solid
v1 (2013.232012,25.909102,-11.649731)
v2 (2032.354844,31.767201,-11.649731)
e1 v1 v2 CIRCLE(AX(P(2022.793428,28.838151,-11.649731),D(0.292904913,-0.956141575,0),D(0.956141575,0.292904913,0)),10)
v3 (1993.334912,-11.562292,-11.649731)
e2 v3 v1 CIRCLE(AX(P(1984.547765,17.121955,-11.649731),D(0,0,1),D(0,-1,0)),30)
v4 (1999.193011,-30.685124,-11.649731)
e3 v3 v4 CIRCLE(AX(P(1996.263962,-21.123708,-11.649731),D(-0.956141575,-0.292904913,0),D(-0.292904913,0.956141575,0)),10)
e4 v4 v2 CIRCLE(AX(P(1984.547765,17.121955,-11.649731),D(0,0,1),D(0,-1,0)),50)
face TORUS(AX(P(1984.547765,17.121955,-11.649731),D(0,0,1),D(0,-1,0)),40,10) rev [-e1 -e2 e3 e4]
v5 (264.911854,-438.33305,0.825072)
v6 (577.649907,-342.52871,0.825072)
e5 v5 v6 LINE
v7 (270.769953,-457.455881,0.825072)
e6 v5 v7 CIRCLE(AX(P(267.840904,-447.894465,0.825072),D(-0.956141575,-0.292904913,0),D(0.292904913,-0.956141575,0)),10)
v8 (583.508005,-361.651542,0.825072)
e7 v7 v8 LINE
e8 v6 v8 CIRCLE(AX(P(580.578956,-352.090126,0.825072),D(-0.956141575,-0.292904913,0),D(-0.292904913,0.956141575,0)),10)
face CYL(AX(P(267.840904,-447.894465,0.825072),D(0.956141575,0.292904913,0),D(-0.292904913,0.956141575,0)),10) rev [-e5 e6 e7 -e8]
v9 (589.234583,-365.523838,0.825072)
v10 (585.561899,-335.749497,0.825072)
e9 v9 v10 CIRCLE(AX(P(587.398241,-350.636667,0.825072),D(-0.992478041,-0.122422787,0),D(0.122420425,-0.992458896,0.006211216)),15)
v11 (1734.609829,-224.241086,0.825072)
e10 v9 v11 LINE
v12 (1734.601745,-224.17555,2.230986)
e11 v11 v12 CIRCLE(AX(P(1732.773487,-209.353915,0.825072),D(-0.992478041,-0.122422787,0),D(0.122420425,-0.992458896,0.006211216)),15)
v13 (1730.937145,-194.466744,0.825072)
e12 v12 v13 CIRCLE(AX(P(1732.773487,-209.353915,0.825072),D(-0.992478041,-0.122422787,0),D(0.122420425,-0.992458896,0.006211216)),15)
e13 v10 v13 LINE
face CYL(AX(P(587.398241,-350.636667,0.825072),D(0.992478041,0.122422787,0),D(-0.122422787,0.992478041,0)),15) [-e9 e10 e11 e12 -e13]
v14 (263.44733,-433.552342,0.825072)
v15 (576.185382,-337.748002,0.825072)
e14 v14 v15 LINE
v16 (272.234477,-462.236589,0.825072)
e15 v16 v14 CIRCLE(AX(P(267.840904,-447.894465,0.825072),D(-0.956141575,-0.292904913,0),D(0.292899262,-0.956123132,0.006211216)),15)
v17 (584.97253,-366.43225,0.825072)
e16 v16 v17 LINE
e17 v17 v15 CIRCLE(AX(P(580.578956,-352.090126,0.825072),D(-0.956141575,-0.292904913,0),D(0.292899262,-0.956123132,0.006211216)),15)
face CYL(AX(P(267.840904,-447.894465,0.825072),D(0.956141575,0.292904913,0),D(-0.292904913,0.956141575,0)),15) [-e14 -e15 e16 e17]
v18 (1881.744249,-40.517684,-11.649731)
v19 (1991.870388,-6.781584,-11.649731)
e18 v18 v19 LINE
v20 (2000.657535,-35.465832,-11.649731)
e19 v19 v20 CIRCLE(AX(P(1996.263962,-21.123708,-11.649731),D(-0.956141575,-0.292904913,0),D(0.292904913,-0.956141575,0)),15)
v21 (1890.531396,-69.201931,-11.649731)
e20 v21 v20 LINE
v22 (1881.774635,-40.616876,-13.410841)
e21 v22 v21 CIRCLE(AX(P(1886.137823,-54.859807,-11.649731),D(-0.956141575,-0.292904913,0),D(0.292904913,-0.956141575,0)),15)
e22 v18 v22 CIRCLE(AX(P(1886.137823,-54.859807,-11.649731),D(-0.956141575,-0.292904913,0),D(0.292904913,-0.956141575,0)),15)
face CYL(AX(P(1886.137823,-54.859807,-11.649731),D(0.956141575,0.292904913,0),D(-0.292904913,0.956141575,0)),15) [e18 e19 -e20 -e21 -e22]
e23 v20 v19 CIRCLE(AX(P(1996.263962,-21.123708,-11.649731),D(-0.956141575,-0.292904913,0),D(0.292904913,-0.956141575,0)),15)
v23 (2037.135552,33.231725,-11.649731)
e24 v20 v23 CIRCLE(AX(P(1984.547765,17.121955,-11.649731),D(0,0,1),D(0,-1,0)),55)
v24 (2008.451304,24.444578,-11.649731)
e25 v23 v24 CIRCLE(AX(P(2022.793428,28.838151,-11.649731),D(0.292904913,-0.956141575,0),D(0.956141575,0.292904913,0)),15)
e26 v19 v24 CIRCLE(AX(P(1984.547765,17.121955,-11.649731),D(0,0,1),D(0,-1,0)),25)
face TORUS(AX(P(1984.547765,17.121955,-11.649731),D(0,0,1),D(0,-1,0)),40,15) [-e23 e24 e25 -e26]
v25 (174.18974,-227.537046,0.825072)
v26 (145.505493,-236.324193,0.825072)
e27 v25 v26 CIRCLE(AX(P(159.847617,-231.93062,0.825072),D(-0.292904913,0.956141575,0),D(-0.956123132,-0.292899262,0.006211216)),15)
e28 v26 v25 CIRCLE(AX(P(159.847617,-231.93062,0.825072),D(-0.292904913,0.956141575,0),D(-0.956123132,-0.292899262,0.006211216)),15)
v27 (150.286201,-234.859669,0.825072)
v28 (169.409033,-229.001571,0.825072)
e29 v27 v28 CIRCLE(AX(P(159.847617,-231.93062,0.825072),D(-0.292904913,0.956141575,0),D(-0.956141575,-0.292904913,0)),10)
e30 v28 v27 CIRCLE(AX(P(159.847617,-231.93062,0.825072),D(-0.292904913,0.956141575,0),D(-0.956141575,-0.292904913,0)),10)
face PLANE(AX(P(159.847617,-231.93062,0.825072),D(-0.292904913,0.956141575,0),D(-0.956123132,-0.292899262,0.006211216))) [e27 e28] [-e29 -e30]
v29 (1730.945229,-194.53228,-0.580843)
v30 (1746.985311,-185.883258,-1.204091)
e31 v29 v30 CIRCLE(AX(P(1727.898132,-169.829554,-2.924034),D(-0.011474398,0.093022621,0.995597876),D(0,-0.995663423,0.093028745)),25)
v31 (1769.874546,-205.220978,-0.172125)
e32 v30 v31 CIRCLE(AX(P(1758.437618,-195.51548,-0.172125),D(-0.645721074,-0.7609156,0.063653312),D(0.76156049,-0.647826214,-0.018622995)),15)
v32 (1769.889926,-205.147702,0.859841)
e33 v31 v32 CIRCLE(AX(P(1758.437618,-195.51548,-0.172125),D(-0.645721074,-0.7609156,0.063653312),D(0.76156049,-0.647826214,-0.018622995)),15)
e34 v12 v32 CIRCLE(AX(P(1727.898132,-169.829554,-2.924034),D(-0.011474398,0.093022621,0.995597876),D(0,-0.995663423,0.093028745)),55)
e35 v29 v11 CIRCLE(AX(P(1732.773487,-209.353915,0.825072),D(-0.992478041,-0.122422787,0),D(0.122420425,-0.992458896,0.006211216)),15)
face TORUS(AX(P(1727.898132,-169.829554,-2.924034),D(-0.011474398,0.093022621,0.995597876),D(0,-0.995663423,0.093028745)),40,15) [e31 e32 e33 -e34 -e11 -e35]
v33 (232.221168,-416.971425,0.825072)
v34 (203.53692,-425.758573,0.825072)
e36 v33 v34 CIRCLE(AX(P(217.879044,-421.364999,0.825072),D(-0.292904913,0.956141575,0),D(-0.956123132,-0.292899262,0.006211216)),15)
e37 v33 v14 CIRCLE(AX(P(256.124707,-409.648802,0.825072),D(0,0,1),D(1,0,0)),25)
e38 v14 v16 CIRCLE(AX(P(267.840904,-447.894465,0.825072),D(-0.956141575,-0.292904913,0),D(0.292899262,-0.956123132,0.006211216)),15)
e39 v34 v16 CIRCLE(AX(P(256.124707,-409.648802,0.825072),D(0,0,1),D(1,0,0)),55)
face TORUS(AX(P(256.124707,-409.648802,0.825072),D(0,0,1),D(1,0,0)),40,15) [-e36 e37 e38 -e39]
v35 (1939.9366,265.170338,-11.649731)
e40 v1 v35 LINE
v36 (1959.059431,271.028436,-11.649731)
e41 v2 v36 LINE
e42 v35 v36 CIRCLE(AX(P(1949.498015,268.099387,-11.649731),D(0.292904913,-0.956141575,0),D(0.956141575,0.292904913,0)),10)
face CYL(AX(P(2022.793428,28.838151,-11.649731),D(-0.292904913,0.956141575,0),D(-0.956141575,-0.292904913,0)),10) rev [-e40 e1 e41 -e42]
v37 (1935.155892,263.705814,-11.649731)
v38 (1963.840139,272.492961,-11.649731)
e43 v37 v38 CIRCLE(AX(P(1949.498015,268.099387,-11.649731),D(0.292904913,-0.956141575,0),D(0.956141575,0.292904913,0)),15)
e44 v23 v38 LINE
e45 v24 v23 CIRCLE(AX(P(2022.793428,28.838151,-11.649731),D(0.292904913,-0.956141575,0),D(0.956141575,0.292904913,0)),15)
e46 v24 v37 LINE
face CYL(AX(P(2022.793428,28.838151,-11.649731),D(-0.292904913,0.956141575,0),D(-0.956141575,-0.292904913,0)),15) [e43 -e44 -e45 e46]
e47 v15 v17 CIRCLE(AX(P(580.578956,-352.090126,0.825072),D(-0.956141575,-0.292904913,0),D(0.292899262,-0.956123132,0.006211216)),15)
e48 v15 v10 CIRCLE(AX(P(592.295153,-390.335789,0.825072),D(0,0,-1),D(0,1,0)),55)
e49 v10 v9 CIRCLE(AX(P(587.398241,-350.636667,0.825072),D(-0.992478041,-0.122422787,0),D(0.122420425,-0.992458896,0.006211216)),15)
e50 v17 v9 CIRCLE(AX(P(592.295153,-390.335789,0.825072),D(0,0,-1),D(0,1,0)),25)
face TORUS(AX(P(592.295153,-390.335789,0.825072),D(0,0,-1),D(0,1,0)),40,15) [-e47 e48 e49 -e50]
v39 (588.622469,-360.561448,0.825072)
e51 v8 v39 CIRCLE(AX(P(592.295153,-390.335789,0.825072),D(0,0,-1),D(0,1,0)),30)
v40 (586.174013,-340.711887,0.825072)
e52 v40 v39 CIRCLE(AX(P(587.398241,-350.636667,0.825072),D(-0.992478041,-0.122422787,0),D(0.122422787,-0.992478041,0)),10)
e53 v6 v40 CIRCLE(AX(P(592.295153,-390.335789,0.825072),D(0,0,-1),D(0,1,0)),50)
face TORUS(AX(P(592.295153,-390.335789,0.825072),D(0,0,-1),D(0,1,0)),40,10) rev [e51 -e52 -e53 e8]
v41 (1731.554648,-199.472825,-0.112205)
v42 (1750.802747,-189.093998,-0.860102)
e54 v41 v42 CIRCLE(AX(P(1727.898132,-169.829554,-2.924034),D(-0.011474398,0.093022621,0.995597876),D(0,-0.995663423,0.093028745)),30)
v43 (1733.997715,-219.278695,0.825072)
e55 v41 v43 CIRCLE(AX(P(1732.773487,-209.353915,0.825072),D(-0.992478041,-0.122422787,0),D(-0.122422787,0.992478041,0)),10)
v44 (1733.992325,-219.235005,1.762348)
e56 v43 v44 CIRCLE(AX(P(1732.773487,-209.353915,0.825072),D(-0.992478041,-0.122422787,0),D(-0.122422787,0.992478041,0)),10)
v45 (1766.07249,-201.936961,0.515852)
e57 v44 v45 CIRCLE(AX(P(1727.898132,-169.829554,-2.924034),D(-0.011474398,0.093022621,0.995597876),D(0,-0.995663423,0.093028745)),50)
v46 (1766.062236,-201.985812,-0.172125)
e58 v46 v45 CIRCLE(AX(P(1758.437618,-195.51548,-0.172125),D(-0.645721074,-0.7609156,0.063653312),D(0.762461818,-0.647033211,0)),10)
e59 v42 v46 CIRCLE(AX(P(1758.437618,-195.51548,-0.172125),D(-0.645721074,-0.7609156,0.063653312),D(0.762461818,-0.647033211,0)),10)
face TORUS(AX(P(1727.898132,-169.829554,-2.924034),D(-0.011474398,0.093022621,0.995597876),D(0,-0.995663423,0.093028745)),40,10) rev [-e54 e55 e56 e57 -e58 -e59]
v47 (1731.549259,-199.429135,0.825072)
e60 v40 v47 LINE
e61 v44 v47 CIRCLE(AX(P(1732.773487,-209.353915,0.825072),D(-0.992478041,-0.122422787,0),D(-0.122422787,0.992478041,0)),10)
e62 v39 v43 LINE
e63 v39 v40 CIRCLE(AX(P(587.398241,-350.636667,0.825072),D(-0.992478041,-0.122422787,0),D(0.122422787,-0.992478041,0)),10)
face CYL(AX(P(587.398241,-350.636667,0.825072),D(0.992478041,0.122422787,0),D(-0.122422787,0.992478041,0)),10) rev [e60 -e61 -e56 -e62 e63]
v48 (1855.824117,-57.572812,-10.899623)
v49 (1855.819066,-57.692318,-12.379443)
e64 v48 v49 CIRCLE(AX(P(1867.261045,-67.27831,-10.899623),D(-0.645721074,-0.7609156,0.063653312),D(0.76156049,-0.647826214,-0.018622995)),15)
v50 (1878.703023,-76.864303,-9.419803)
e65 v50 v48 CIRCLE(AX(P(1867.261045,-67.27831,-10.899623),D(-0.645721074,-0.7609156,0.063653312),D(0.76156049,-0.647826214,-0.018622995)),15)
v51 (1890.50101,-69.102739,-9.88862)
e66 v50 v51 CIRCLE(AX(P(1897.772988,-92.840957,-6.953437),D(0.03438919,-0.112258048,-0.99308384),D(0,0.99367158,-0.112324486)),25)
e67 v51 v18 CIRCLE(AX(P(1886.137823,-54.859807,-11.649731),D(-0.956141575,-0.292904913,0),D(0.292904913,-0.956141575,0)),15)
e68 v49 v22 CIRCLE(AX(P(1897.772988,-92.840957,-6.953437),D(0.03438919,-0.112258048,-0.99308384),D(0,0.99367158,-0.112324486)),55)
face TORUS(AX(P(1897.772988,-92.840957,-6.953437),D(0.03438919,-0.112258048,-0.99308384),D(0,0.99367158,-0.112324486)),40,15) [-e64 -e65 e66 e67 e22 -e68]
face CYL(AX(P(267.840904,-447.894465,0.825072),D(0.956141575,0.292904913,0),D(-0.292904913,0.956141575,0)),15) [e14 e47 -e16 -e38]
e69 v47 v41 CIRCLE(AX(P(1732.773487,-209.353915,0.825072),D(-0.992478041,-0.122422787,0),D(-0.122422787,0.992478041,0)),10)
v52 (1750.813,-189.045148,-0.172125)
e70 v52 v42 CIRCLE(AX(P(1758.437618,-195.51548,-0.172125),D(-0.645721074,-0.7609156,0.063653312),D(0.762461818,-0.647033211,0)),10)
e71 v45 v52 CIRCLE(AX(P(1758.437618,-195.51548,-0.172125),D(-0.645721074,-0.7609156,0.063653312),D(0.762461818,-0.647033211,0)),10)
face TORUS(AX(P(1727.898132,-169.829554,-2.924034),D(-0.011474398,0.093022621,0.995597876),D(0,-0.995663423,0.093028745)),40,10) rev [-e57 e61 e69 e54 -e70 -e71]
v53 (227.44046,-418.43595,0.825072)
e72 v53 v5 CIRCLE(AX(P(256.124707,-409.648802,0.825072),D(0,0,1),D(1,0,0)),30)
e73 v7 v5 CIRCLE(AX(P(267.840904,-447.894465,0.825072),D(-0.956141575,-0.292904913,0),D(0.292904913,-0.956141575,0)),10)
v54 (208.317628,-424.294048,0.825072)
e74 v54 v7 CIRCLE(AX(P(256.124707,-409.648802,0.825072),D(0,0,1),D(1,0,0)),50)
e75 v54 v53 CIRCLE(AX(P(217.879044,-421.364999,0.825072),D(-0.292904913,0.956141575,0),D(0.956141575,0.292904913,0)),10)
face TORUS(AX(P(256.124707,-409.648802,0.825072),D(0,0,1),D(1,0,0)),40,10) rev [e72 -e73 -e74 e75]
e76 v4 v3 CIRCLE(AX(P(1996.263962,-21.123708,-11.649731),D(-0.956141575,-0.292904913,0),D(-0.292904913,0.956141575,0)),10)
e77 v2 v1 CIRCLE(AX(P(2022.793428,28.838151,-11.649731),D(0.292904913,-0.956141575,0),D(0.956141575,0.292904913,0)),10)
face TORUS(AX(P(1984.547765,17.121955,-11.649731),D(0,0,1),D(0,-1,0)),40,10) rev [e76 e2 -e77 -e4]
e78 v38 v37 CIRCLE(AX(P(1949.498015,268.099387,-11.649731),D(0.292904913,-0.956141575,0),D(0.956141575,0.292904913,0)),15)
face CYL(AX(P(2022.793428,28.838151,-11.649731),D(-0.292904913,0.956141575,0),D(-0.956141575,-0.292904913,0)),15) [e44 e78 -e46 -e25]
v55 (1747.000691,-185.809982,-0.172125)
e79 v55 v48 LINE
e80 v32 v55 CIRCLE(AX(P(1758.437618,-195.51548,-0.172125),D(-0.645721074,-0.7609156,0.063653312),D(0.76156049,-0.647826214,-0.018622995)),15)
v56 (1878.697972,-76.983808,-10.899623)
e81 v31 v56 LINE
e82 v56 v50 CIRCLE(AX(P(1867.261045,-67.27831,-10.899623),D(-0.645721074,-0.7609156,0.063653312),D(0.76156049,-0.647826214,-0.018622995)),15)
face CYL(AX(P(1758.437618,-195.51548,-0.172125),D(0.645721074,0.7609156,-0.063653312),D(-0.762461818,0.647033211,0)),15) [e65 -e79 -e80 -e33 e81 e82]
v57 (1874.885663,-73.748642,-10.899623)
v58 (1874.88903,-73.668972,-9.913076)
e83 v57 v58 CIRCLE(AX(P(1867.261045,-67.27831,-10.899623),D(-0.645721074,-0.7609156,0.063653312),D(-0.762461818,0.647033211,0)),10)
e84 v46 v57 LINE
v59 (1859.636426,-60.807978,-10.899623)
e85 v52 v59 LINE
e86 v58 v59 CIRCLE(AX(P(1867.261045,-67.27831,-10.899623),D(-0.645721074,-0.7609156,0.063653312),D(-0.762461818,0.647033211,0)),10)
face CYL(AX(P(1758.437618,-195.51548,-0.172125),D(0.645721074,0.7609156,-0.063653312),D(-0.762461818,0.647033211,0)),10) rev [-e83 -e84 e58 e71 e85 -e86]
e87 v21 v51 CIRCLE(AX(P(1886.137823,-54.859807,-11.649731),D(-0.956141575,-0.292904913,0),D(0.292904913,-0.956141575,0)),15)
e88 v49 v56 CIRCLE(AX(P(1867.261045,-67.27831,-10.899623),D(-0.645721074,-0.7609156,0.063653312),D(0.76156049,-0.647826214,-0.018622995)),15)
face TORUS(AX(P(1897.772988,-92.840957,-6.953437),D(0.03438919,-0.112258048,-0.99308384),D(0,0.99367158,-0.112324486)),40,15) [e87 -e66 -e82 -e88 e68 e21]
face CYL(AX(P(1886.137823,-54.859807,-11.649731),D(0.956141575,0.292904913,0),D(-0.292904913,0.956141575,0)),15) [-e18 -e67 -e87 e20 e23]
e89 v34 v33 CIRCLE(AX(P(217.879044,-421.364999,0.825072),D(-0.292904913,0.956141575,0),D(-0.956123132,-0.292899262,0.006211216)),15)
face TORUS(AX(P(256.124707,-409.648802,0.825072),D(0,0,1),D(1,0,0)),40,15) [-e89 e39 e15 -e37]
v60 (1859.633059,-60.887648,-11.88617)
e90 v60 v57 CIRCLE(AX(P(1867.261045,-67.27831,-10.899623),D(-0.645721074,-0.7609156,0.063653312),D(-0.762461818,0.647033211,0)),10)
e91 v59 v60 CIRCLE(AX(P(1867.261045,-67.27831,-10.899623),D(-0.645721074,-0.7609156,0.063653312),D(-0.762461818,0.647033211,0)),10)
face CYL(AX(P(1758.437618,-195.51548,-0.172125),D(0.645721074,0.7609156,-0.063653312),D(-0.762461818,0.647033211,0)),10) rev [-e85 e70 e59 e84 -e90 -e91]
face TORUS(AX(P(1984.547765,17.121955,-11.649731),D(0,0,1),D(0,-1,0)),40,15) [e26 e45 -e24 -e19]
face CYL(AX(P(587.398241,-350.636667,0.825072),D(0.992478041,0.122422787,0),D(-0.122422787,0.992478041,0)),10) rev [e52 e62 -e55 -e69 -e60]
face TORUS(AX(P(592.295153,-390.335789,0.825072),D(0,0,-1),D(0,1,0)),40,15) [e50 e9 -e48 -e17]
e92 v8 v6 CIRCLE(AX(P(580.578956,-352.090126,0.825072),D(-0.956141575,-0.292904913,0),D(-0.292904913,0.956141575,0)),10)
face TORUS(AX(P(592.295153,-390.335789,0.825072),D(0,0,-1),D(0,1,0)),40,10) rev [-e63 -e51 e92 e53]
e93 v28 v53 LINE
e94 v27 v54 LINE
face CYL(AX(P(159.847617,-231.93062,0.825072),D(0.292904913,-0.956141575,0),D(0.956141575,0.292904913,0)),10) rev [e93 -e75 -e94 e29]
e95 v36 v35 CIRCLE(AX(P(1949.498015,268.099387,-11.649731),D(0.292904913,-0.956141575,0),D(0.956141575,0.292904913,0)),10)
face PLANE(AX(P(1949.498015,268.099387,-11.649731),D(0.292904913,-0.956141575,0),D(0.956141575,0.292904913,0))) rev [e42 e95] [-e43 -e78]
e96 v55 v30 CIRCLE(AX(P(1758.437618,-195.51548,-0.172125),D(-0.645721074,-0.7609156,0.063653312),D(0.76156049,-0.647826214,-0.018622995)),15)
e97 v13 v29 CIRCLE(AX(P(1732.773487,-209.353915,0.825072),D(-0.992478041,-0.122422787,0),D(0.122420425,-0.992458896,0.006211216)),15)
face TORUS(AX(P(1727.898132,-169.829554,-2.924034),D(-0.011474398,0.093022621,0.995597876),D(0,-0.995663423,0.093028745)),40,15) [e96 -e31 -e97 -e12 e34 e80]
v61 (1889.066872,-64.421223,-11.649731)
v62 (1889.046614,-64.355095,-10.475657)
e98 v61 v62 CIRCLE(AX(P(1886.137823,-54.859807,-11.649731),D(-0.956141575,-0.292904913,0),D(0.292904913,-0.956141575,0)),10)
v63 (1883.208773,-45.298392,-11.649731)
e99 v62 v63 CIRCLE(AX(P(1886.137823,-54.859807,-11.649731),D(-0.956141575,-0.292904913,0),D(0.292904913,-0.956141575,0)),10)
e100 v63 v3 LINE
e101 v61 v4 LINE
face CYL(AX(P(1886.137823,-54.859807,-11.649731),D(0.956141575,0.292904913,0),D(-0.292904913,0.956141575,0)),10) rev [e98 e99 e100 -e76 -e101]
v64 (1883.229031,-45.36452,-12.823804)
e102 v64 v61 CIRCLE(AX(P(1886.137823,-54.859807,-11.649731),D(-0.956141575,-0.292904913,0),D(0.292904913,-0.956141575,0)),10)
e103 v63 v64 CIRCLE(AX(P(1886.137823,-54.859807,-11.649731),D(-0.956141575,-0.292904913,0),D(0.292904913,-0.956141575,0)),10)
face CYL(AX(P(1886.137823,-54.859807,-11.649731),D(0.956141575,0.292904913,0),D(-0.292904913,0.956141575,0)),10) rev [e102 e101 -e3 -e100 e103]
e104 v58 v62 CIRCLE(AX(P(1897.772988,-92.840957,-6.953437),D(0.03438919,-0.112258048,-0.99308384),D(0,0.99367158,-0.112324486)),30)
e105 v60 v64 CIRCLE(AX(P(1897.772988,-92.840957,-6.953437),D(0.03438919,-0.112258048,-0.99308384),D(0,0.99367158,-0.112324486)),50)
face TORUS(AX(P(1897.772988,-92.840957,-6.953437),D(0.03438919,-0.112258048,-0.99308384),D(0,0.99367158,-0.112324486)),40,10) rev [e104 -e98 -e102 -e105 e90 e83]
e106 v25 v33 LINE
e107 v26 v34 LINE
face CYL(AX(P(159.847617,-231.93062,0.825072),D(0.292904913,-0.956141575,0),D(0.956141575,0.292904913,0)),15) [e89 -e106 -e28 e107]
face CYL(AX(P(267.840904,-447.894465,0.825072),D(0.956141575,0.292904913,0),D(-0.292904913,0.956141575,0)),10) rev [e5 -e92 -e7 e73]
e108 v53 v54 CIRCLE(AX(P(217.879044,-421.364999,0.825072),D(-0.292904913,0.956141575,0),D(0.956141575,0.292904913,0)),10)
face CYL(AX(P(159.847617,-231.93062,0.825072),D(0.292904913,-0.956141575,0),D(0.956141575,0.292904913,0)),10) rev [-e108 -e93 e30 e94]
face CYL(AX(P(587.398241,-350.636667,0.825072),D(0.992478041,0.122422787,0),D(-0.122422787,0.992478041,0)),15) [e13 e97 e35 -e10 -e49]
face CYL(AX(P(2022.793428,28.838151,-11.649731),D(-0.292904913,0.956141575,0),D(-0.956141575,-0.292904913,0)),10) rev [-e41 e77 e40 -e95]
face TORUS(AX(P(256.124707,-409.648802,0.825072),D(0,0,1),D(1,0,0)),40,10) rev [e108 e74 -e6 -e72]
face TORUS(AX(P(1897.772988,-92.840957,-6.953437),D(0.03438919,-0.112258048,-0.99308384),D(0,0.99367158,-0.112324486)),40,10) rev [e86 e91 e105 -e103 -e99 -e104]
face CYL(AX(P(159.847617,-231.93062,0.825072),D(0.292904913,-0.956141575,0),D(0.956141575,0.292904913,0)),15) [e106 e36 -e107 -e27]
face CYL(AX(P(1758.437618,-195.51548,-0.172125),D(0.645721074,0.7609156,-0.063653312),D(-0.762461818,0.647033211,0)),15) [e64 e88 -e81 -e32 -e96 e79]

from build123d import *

# Parameters (mm, degrees)
SWEEP_THIN1_PROFILE_R   = 15
SWEEP_THIN1_PROFILE_R_2 = 10


with BuildPart() as part:
    # Sweep-Thin1: sweep along a curve in space
    with BuildLine() as sweep_thin1_path:
        Line((2022.793428066, 28.838151427, -11.649730724), (1949.498015394, 268.099387204, -11.649730724))
        ThreePointArc((1996.263961553, -21.123708091, -11.649730724), (2019.876134716, -1.637210748, -11.649730724), (2022.793428066, 28.838151427, -11.649730724))
        Line((1886.137822525, -54.859807379, -11.649730724), (1996.263961553, -21.123708091, -11.649730724))
        ThreePointArc((1867.261044608, -67.278310178, -10.899623065), (1875.803940416, -59.718953476, -11.458302347), (1886.137822525, -54.859807379, -11.649730724))
        Line((1758.437618296, -195.5154797, -0.172125022), (1867.261044608, -67.278310178, -10.899623065))
        ThreePointArc((1732.773486814, -209.353915035, 0.825071817), (1746.915200671, -204.846187229, 0.566882239), (1758.437618296, -195.5154797, -0.172125022))
        Line((587.398241077, -350.636667449, 0.825071817), (1732.773486814, -209.353915035, 0.825071817))
        ThreePointArc((580.57895604, -352.090126062, 0.825071817), (583.956868872, -351.214528548, 0.825071817), (587.398241077, -350.636667449, 0.825071817))
        Line((580.57895604, -352.090126062, 0.825071817), (267.840903589, -447.894465358, 0.825071817))
        ThreePointArc((267.840903589, -447.894465358, 0.825071817), (237.365541414, -444.977172008, 0.825071817), (217.879044071, -421.364998844, 0.825071817))
        Line((217.879044071, -421.364998844, 0.825071817), (159.847616861, -231.930619776, 0.825071817))
    # Sweep-Thin1 profile (on start of the path) → Sweep-Thin1 (sweep)
    with BuildSketch(Plane(origin=(159.847616861, -231.930619776, 0.825071817), x_dir=(-0.9561415753975281, -0.2929049125507002, 0), z_dir=(0.2929049125507002, -0.9561415753975281, -2.7998246546986226e-14))):
        Circle(SWEEP_THIN1_PROFILE_R)
        Circle(SWEEP_THIN1_PROFILE_R_2, mode=Mode.SUBTRACT)
    sweep(path=sweep_thin1_path.line)


solid = part.part
